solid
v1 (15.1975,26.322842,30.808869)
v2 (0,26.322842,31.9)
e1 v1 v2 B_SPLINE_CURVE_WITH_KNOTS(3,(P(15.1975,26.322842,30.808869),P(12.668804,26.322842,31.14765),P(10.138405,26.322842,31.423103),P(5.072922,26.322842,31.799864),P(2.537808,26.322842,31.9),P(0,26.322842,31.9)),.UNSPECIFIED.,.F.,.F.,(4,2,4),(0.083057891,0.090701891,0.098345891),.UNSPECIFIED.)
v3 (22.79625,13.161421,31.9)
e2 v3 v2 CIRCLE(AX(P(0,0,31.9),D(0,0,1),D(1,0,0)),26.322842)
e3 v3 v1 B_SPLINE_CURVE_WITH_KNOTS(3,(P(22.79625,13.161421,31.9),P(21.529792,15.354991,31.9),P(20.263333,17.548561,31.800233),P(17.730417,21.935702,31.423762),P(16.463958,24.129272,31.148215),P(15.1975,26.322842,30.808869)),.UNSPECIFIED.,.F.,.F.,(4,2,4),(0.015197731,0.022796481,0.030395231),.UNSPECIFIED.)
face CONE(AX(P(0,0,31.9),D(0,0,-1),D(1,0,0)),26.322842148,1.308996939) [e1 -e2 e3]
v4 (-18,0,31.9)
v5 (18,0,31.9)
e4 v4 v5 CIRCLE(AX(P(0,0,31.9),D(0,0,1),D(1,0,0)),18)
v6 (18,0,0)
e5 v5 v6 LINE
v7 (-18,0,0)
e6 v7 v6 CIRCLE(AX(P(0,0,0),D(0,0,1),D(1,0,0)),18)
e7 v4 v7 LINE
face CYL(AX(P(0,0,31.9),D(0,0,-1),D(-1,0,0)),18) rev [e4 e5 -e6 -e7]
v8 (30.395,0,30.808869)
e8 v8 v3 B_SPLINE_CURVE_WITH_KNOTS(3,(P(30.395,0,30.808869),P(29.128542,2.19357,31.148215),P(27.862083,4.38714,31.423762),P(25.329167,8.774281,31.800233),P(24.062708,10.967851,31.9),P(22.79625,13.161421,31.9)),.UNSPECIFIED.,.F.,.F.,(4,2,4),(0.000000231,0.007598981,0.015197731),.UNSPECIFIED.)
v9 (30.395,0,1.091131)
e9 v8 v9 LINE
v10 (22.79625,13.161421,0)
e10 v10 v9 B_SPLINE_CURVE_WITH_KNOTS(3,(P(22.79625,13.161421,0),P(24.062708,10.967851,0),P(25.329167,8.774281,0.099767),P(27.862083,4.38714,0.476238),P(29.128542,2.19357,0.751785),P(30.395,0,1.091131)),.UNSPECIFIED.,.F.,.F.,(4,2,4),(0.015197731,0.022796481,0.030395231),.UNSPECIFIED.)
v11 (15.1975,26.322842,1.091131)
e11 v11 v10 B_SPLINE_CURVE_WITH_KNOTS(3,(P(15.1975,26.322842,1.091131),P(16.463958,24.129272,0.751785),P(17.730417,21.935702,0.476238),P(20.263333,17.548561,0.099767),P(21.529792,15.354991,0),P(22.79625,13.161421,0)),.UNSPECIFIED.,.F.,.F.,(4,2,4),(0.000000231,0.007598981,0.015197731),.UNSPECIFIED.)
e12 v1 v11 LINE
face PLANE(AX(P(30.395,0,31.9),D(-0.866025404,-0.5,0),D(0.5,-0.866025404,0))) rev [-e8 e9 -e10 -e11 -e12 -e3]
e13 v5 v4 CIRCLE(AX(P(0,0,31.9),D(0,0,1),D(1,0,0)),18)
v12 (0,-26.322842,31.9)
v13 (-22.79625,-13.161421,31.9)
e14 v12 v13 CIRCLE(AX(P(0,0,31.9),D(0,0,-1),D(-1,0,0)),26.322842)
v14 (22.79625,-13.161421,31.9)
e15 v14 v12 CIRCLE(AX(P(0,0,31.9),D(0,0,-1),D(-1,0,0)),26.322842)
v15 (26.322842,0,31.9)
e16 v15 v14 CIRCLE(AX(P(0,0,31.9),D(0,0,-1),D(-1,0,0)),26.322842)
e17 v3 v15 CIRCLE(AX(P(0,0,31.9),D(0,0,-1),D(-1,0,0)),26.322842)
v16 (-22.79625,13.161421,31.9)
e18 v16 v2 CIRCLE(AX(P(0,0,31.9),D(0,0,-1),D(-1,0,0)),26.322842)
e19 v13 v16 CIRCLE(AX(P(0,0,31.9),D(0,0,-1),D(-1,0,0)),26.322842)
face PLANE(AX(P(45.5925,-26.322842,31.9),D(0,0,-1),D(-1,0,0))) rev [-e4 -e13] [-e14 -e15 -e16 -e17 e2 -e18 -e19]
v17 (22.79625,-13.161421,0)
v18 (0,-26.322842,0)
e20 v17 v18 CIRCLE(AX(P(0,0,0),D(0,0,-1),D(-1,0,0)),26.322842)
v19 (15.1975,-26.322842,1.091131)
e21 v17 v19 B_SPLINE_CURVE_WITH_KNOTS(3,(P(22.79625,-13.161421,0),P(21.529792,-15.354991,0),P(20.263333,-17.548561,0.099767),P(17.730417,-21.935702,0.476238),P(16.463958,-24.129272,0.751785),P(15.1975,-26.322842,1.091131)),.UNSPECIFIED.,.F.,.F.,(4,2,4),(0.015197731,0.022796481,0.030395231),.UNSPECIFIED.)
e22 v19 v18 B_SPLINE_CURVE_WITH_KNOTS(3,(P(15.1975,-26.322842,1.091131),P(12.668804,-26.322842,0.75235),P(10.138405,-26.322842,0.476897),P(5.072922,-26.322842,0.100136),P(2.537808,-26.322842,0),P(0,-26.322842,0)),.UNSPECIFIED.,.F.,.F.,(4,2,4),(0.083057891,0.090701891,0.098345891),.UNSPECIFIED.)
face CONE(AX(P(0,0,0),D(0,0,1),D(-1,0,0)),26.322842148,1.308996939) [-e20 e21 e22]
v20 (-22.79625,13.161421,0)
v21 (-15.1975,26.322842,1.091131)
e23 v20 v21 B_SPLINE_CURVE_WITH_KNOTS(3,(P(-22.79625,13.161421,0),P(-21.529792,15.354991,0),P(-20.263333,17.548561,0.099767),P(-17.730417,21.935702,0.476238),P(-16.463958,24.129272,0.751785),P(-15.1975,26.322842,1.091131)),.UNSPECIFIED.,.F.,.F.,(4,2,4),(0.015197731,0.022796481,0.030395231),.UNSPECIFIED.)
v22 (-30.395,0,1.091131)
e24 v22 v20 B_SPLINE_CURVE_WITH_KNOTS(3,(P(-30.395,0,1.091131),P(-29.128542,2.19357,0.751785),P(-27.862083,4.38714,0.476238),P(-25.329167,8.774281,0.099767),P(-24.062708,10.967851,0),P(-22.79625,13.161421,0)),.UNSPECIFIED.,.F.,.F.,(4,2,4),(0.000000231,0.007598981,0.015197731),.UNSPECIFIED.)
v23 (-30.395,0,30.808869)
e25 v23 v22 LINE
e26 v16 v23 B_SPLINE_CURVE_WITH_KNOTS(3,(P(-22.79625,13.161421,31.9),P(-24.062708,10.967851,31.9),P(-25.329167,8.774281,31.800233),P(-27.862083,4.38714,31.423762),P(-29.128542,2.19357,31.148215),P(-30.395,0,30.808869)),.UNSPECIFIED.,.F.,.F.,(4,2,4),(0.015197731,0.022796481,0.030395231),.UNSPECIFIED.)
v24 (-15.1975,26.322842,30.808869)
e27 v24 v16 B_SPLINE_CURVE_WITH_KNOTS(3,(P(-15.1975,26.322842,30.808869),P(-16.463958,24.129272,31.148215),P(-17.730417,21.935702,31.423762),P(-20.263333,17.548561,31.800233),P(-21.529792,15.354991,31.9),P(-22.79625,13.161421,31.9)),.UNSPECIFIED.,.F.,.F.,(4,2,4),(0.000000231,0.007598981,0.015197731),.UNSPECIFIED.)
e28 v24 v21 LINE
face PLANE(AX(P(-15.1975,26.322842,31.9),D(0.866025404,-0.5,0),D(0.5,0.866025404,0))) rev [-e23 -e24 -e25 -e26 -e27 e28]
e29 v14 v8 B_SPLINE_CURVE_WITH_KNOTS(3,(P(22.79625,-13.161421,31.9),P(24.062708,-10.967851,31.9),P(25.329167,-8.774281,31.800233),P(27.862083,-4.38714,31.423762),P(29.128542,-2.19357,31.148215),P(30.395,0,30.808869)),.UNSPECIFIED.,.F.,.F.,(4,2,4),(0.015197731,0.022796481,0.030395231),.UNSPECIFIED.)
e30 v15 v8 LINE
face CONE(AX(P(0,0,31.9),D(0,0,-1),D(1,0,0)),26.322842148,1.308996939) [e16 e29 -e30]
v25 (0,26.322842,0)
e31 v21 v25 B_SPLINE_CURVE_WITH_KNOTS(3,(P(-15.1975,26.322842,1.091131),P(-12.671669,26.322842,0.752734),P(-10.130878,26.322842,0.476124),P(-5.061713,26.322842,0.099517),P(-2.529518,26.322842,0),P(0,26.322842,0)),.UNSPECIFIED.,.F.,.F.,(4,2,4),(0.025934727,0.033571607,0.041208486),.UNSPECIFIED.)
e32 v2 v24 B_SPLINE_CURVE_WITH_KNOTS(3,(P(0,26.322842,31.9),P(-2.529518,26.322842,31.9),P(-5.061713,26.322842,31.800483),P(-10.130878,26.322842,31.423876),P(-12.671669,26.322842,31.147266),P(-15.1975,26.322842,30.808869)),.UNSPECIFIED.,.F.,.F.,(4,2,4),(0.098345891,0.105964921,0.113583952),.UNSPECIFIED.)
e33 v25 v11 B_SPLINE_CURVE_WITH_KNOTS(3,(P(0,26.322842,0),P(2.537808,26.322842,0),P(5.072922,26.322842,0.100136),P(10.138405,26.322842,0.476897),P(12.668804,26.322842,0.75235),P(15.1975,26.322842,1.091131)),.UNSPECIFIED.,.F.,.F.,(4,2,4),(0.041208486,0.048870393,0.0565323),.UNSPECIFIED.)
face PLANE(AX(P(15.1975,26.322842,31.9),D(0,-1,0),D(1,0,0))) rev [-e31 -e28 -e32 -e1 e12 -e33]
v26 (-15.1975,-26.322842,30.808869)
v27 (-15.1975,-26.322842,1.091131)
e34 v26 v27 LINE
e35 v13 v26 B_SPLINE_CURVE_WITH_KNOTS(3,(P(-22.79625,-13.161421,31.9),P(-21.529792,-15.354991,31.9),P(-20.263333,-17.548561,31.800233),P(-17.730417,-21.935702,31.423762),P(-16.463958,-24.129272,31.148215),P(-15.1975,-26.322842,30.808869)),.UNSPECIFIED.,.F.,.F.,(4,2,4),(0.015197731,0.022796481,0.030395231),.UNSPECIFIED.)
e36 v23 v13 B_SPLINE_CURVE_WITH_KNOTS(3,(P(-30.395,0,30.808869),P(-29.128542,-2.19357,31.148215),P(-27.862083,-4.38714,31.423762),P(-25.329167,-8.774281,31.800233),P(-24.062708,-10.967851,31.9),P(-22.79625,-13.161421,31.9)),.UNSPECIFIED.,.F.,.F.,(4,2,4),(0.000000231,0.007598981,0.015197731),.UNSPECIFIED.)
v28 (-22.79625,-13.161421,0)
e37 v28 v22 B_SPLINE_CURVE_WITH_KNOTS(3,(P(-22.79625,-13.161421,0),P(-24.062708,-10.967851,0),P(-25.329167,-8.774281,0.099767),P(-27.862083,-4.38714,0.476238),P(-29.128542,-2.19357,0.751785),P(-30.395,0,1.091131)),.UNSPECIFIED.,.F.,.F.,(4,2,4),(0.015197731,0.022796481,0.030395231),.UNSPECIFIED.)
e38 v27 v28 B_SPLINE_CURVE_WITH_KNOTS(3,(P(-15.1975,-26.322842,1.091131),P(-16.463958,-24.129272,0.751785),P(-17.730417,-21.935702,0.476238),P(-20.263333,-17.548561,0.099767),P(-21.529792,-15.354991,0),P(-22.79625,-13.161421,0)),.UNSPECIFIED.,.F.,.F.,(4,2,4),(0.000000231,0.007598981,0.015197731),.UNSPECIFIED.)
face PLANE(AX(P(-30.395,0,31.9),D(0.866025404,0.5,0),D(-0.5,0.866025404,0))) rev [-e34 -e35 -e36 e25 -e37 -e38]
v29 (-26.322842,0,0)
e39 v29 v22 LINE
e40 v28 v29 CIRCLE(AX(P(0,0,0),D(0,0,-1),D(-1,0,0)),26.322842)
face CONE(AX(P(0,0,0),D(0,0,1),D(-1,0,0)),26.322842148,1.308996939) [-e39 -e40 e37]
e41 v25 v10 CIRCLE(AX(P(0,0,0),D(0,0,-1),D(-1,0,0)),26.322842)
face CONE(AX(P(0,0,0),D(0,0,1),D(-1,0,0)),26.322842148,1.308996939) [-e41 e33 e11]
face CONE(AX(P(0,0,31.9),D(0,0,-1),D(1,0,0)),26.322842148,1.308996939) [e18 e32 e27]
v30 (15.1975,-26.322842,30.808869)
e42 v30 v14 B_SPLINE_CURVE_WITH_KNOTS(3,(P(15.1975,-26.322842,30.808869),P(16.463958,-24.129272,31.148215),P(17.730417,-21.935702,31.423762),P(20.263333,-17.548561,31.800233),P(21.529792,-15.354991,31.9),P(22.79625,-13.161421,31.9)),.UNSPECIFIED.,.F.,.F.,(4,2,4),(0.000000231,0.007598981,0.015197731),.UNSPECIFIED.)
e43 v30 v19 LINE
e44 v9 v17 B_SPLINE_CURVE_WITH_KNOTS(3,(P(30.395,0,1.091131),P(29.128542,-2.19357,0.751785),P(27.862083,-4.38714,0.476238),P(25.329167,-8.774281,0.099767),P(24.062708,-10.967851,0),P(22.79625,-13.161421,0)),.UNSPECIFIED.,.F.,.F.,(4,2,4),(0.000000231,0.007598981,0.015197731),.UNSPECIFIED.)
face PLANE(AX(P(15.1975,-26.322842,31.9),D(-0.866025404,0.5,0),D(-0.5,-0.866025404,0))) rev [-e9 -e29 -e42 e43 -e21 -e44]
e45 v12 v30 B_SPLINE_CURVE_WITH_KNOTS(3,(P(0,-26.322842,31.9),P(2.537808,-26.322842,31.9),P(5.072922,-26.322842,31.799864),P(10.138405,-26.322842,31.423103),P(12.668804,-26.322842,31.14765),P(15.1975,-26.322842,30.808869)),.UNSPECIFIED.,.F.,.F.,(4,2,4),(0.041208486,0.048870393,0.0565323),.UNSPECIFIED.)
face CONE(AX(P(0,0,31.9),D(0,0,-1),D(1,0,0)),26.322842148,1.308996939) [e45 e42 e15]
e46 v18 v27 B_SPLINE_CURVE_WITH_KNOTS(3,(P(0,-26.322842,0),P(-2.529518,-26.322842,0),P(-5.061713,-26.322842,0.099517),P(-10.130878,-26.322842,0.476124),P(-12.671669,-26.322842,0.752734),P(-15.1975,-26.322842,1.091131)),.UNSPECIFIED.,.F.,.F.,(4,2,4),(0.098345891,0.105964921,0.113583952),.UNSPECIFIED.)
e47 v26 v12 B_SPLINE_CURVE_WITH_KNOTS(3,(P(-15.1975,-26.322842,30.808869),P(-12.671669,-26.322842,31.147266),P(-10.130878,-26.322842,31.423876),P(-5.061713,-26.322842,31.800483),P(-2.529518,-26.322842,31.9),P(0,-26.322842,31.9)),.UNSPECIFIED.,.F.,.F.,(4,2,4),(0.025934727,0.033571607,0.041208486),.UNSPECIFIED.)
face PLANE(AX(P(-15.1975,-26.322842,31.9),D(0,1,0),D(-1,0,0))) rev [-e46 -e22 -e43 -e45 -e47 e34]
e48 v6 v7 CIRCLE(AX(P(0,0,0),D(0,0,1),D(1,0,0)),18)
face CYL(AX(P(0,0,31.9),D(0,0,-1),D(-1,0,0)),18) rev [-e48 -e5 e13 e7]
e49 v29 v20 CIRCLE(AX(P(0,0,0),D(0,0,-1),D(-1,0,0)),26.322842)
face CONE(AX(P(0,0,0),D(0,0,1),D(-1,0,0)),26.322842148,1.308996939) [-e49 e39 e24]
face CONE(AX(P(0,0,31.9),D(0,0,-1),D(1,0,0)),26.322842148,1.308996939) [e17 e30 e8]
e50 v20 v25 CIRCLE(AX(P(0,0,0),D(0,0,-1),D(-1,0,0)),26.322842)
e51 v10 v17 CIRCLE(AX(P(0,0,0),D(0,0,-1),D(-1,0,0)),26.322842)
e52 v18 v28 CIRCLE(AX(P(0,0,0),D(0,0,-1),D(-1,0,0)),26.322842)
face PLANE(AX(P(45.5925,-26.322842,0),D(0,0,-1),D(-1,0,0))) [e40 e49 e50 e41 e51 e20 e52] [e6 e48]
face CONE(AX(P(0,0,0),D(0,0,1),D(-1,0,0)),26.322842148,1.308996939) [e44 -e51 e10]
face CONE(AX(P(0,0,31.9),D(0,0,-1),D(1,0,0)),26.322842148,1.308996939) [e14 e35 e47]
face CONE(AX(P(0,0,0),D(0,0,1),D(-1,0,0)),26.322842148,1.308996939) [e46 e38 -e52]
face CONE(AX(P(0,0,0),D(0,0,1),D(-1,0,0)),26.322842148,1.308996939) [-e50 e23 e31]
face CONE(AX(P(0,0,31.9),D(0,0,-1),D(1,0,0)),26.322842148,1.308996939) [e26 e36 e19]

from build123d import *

# Parameters (mm, degrees)
SKETCH_1_R          = 18
EXTRUDE_519_DEPTH   = 31.9
SKETCH_2_OUTSIDE_W  = 363.728
SKETCH_2_OUTSIDE_H  = 355.584
SKETCH_2_OUTSIDE_R  = 26.322842148
CUT_EXTRUDE_1_DEPTH = 38
CUT_EXTRUDE_1_DRAFT = -75
SKETCH_3_OUTSIDE_W  = 363.728
SKETCH_3_OUTSIDE_H  = 355.584
SKETCH_3_OUTSIDE_R  = 26.322842148
CUT_EXTRUDE_2_DEPTH = 38
CUT_EXTRUDE_2_DRAFT = -75


with BuildPart() as part:
    # 草图1 → Extrude 519 (new body)
    with BuildSketch(Plane.XY):
        Polygon((15.1975, 26.322842148), (-15.1975, 26.322842148), (-30.395, 0), (-15.1975, -26.322842148), (15.1975, -26.322842148), (30.395, 0), align=None)
        Circle(SKETCH_1_R, mode=Mode.SUBTRACT)
    extrude(amount=EXTRUDE_519_DEPTH)


with BuildPart() as cut_extrude_1_tool:
    # 草图2 outside → 切除-拉伸1 (with draft: the straight prism first)
    with BuildSketch(Plane(origin=(0, 0, 0), x_dir=(-1, 0, 0), z_dir=(0, 0, -1))):
        Rectangle(SKETCH_2_OUTSIDE_W, SKETCH_2_OUTSIDE_H)
        Circle(SKETCH_2_OUTSIDE_R, mode=Mode.SUBTRACT)
    extrude(amount=-CUT_EXTRUDE_1_DEPTH)
    # 切除-拉伸1: the draft: its side faces are tilted about the plane it starts from
    cut_extrude_1_sides = [cut_extrude_1_tool.faces().sort_by_distance(p)[0] for p in [
        (0, -177.792, 19),
        (-181.864, 0, 19),
        (0, 177.792, 19),
        (181.864, 0, 19),
        (26.322842148, 0, 19),
    ]]
    draft(cut_extrude_1_sides, Plane(origin=(0, 0, 0), x_dir=(-1, 0, 0), z_dir=(0, 0, -1)), CUT_EXTRUDE_1_DRAFT)


with BuildPart() as part_1:
    add(part.part)

    # 切除-拉伸1: cut by cut_extrude_1_tool
    add(cut_extrude_1_tool.part, mode=Mode.SUBTRACT)


with BuildPart() as cut_extrude_2_tool:
    # 草图3 outside → 切除-拉伸2 (with draft: the straight prism first)
    with BuildSketch(Plane.XY.offset(31.9)):
        Rectangle(SKETCH_3_OUTSIDE_W, SKETCH_3_OUTSIDE_H)
        Circle(SKETCH_3_OUTSIDE_R, mode=Mode.SUBTRACT)
    extrude(amount=-CUT_EXTRUDE_2_DEPTH)
    # 切除-拉伸2: the draft: its side faces are tilted about the plane it starts from
    cut_extrude_2_sides = [cut_extrude_2_tool.faces().sort_by_distance(p)[0] for p in [
        (0, -177.792, 12.9),
        (181.864, 0, 12.9),
        (0, 177.792, 12.9),
        (-181.864, 0, 12.9),
        (-26.322842148, 0, 12.9),
    ]]
    draft(cut_extrude_2_sides, Plane.XY.offset(31.9), CUT_EXTRUDE_2_DRAFT)


with BuildPart() as part_2:
    add(part_1.part)

    # 切除-拉伸2: cut by cut_extrude_2_tool
    add(cut_extrude_2_tool.part, mode=Mode.SUBTRACT)


solid = part_2.part
